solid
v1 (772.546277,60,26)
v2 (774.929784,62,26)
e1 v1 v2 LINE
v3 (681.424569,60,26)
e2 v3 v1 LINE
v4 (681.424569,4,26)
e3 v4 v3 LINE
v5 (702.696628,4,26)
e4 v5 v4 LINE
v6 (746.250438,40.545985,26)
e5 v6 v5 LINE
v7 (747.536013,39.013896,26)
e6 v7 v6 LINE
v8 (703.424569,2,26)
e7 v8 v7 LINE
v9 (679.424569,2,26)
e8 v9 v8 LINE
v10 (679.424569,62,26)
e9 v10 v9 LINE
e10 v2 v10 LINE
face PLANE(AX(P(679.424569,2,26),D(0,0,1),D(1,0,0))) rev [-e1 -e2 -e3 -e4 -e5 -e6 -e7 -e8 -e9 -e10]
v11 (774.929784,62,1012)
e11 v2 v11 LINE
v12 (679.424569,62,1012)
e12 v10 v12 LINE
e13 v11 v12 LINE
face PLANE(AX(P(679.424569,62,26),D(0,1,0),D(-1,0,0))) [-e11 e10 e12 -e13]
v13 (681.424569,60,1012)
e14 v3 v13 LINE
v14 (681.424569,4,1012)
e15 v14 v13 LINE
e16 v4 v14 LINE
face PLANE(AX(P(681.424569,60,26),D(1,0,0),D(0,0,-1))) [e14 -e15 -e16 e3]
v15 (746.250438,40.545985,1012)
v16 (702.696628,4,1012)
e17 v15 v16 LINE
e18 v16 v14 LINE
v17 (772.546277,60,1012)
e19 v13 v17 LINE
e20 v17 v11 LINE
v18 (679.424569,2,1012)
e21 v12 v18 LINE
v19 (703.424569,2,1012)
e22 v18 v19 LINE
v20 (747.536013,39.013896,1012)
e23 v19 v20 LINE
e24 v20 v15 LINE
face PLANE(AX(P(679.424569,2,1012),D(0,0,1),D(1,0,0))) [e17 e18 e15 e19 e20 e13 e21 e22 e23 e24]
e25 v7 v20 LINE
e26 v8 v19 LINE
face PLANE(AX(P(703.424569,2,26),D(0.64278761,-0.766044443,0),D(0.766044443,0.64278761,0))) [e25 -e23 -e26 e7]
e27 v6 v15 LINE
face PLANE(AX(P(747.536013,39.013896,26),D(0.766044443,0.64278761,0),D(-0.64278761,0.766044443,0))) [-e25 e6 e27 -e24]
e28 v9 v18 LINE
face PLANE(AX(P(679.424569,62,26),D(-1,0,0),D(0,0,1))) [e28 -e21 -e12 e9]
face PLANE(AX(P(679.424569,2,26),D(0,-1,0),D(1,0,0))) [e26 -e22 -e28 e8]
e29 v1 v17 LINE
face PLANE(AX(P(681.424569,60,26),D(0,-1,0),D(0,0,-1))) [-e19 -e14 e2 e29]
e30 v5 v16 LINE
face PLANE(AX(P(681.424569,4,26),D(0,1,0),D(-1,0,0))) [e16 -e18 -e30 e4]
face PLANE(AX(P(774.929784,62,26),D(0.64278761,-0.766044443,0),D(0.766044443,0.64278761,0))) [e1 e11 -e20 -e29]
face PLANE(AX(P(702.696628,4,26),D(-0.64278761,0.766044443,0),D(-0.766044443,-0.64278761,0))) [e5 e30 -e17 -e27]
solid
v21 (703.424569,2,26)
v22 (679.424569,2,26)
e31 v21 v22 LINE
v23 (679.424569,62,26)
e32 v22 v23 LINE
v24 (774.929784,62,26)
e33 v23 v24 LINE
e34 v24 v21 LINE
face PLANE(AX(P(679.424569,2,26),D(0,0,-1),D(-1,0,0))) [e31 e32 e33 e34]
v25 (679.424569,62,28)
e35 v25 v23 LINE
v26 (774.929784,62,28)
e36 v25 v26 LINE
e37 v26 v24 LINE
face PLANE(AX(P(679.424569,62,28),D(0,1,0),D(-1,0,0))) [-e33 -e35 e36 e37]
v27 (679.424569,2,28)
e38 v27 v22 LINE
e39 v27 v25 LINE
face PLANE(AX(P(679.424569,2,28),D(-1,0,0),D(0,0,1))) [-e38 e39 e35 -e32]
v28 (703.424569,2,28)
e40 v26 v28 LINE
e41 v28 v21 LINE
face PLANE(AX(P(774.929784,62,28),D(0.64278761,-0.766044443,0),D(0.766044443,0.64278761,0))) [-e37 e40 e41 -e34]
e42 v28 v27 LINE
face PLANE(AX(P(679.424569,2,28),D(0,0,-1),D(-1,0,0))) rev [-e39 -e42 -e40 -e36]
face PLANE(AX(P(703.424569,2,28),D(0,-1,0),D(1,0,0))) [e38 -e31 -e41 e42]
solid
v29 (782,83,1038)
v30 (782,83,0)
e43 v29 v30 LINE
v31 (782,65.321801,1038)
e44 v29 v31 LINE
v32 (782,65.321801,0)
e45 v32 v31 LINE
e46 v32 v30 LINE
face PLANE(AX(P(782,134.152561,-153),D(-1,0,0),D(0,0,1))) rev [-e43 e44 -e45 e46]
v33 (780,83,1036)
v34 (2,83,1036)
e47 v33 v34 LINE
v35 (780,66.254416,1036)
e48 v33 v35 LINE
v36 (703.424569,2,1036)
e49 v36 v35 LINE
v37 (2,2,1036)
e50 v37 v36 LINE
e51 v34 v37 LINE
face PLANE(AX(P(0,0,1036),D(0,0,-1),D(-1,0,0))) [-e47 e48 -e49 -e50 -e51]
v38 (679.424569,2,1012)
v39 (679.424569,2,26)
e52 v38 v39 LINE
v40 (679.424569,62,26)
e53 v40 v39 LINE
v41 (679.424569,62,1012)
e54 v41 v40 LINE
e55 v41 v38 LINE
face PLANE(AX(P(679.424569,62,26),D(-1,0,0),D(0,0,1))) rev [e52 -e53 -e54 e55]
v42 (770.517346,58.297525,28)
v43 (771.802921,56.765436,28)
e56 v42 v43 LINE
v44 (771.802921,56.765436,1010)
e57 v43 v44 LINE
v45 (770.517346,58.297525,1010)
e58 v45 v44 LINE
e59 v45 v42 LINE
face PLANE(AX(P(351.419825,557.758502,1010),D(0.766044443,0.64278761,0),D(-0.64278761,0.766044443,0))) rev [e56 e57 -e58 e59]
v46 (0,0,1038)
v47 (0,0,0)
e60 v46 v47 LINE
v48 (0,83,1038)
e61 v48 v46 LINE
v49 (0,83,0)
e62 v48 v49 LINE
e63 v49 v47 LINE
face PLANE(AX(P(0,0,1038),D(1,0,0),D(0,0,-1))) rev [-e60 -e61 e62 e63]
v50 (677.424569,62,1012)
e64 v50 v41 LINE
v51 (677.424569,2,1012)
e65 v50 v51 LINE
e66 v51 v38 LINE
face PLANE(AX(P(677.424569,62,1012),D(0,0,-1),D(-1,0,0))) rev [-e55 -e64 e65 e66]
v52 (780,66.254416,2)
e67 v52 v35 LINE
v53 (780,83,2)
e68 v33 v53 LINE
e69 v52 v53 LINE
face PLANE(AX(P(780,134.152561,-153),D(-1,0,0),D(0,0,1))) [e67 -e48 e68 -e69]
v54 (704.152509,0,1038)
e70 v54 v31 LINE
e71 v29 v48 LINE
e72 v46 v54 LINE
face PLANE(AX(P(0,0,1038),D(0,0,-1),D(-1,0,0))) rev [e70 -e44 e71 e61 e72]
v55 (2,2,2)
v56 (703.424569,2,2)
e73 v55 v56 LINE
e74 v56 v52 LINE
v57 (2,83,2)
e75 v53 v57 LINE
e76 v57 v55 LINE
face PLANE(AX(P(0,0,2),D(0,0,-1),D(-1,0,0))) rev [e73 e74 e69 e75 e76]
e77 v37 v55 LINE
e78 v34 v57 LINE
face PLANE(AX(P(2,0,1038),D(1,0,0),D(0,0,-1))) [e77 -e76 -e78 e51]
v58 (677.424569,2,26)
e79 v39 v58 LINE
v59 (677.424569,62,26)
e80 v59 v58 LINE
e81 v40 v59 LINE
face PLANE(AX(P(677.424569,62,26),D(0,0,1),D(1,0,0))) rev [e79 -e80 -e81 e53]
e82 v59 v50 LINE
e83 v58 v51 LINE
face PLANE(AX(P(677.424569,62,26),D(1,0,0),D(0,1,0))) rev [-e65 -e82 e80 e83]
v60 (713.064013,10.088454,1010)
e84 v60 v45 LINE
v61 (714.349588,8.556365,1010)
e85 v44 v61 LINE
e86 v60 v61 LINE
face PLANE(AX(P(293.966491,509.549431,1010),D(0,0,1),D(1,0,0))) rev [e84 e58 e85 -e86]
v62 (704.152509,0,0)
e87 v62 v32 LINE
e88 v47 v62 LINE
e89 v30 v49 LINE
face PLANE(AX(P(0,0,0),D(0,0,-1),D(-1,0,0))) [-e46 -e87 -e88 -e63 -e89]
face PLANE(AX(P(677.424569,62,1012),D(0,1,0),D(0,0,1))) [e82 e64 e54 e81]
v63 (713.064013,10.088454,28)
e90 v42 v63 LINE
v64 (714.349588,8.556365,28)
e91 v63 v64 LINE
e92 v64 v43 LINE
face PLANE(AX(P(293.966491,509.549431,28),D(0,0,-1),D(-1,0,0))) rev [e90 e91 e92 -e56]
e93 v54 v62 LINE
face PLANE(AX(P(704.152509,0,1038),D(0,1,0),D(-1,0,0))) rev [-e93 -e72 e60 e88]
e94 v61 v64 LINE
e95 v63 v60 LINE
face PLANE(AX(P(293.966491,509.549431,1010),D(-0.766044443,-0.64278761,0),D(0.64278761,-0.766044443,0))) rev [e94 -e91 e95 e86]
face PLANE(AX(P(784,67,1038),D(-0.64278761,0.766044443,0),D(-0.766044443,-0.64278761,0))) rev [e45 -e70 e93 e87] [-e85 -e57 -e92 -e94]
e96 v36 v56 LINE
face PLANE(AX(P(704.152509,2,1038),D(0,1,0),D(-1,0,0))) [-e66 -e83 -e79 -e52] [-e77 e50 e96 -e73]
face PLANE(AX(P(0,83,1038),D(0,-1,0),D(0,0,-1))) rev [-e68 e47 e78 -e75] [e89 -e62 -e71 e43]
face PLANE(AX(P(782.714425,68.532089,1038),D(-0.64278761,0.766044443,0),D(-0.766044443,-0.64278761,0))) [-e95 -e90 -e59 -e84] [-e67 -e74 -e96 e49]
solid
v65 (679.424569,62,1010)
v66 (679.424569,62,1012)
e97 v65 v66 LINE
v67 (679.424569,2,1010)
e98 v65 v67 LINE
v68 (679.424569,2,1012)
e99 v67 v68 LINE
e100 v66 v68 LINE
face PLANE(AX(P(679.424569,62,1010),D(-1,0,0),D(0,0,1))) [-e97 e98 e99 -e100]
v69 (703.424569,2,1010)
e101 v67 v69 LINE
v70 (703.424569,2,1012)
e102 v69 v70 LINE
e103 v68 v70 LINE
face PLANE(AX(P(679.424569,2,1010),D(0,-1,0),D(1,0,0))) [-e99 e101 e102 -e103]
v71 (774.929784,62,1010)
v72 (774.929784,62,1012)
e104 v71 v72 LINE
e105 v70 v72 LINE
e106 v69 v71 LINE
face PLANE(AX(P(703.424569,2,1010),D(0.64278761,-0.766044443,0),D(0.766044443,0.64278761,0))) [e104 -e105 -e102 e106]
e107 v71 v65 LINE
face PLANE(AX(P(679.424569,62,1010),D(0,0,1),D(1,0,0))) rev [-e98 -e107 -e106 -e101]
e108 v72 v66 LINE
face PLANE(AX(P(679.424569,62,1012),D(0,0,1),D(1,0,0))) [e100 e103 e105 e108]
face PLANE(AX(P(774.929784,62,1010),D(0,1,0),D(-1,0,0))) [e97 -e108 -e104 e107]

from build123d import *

# Parameters (mm, degrees)
EXTRUDE_1_DEPTH      = 1038
SKETCH_8_W           = 110.00435438
SKETCH_8_H           = 134.15256119
CUT_EXTRUDE_2_DEPTH  = 1191
SHELL_1_T            = -2
SKETCH_3_W           = 75
SKETCH_3_H           = 982
CUT_EXTRUDE_1_DEPTH  = 654
SKETCH_5_W           = 2
SKETCH_5_H           = 986
EXTRUDE_2_DEPTH      = 60
EXTRUDE_3_DEPTH      = 493
EXTRUDE_3_DEPTH_BACK = 493
EXTRUDE_5_DEPTH      = 2
EXTRUDE_6_DEPTH      = 2


with BuildPart() as part:
    # 草图2 → 凸台-拉伸1 (new body)
    with BuildSketch(Plane.XY):
        Polygon((0, 0), (0, 83), (784, 83), (784, 67), (704.152509296, 0), align=None)
    extrude(amount=EXTRUDE_1_DEPTH)

    # 草图8 → 切除-拉伸2 (cut)
    with BuildSketch(Plane.XY.offset(1038)):
        with Locations((837.00217719, 67.076280595)):
            Rectangle(SKETCH_8_W, SKETCH_8_H)
    extrude(amount=-CUT_EXTRUDE_2_DEPTH, mode=Mode.SUBTRACT)

    # 抽壳1
    shell_1_openings = [part.faces().sort_by_distance(p)[0] for p in [
        (391, 83, 519),
    ]]
    offset(amount=SHELL_1_T, openings=shell_1_openings, kind=Kind.INTERSECTION)

    # 草图3 → 切除-拉伸1 (cut)
    with BuildSketch(Plane(origin=(290.938854629, -346.727425229, 0), x_dir=(0.7660444431189772, 0.6427876096865405, 0), z_dir=(0.6427876096865404, -0.7660444431189772, 0))):
        with Locations((590.223457765, 519)):
            Rectangle(SKETCH_3_W, SKETCH_3_H)
    extrude(amount=-CUT_EXTRUDE_1_DEPTH, mode=Mode.SUBTRACT)

    # 草图5 → 凸台-拉伸2 (add)
    with BuildSketch(Plane(origin=(0, 2, 0), x_dir=(1, 0, 0), z_dir=(0, 1, 0))):
        with Locations((678.424568828, -519)):
            Rectangle(SKETCH_5_W, SKETCH_5_H)
    extrude(amount=EXTRUDE_2_DEPTH)


with BuildPart() as body_2:
    # 草图6 → 凸台-拉伸3 (new, two sides: drawn at the far end of the back side and taken through both)
    with BuildSketch(Plane.XY.offset(519).offset(-EXTRUDE_3_DEPTH_BACK)):
        Polygon((679.424568828, 62), (774.929784383, 62), (772.546277198, 60), (681.424568828, 60), (681.424568828, 4), (702.696628359, 4), (746.250437533, 40.545985214), (747.536012752, 39.013896328), (703.424568828, 2), (679.424568828, 2), align=None)
    extrude(amount=EXTRUDE_3_DEPTH + EXTRUDE_3_DEPTH_BACK)


with BuildPart() as body_3:
    # 草图9 → 凸台-拉伸5 (new body)
    with BuildSketch(Plane.XY.offset(1012)):
        Polygon((679.424568828, 62), (679.424568828, 2), (703.424568828, 2), (774.929784383, 62), align=None)
    extrude(amount=-EXTRUDE_5_DEPTH)


with BuildPart() as body_4:
    # 草图10 → 凸台-拉伸6 (new body)
    with BuildSketch(Plane(origin=(0, 0, 26), x_dir=(-1, 0, 0), z_dir=(0, 0, -1))):
        Polygon((-679.424568828, 2), (-679.424568828, 62), (-774.929784383, 62), (-703.424568828, 2), align=None)
    extrude(amount=-EXTRUDE_6_DEPTH)


solid = Compound([part.part, body_2.part, body_3.part, body_4.part])
